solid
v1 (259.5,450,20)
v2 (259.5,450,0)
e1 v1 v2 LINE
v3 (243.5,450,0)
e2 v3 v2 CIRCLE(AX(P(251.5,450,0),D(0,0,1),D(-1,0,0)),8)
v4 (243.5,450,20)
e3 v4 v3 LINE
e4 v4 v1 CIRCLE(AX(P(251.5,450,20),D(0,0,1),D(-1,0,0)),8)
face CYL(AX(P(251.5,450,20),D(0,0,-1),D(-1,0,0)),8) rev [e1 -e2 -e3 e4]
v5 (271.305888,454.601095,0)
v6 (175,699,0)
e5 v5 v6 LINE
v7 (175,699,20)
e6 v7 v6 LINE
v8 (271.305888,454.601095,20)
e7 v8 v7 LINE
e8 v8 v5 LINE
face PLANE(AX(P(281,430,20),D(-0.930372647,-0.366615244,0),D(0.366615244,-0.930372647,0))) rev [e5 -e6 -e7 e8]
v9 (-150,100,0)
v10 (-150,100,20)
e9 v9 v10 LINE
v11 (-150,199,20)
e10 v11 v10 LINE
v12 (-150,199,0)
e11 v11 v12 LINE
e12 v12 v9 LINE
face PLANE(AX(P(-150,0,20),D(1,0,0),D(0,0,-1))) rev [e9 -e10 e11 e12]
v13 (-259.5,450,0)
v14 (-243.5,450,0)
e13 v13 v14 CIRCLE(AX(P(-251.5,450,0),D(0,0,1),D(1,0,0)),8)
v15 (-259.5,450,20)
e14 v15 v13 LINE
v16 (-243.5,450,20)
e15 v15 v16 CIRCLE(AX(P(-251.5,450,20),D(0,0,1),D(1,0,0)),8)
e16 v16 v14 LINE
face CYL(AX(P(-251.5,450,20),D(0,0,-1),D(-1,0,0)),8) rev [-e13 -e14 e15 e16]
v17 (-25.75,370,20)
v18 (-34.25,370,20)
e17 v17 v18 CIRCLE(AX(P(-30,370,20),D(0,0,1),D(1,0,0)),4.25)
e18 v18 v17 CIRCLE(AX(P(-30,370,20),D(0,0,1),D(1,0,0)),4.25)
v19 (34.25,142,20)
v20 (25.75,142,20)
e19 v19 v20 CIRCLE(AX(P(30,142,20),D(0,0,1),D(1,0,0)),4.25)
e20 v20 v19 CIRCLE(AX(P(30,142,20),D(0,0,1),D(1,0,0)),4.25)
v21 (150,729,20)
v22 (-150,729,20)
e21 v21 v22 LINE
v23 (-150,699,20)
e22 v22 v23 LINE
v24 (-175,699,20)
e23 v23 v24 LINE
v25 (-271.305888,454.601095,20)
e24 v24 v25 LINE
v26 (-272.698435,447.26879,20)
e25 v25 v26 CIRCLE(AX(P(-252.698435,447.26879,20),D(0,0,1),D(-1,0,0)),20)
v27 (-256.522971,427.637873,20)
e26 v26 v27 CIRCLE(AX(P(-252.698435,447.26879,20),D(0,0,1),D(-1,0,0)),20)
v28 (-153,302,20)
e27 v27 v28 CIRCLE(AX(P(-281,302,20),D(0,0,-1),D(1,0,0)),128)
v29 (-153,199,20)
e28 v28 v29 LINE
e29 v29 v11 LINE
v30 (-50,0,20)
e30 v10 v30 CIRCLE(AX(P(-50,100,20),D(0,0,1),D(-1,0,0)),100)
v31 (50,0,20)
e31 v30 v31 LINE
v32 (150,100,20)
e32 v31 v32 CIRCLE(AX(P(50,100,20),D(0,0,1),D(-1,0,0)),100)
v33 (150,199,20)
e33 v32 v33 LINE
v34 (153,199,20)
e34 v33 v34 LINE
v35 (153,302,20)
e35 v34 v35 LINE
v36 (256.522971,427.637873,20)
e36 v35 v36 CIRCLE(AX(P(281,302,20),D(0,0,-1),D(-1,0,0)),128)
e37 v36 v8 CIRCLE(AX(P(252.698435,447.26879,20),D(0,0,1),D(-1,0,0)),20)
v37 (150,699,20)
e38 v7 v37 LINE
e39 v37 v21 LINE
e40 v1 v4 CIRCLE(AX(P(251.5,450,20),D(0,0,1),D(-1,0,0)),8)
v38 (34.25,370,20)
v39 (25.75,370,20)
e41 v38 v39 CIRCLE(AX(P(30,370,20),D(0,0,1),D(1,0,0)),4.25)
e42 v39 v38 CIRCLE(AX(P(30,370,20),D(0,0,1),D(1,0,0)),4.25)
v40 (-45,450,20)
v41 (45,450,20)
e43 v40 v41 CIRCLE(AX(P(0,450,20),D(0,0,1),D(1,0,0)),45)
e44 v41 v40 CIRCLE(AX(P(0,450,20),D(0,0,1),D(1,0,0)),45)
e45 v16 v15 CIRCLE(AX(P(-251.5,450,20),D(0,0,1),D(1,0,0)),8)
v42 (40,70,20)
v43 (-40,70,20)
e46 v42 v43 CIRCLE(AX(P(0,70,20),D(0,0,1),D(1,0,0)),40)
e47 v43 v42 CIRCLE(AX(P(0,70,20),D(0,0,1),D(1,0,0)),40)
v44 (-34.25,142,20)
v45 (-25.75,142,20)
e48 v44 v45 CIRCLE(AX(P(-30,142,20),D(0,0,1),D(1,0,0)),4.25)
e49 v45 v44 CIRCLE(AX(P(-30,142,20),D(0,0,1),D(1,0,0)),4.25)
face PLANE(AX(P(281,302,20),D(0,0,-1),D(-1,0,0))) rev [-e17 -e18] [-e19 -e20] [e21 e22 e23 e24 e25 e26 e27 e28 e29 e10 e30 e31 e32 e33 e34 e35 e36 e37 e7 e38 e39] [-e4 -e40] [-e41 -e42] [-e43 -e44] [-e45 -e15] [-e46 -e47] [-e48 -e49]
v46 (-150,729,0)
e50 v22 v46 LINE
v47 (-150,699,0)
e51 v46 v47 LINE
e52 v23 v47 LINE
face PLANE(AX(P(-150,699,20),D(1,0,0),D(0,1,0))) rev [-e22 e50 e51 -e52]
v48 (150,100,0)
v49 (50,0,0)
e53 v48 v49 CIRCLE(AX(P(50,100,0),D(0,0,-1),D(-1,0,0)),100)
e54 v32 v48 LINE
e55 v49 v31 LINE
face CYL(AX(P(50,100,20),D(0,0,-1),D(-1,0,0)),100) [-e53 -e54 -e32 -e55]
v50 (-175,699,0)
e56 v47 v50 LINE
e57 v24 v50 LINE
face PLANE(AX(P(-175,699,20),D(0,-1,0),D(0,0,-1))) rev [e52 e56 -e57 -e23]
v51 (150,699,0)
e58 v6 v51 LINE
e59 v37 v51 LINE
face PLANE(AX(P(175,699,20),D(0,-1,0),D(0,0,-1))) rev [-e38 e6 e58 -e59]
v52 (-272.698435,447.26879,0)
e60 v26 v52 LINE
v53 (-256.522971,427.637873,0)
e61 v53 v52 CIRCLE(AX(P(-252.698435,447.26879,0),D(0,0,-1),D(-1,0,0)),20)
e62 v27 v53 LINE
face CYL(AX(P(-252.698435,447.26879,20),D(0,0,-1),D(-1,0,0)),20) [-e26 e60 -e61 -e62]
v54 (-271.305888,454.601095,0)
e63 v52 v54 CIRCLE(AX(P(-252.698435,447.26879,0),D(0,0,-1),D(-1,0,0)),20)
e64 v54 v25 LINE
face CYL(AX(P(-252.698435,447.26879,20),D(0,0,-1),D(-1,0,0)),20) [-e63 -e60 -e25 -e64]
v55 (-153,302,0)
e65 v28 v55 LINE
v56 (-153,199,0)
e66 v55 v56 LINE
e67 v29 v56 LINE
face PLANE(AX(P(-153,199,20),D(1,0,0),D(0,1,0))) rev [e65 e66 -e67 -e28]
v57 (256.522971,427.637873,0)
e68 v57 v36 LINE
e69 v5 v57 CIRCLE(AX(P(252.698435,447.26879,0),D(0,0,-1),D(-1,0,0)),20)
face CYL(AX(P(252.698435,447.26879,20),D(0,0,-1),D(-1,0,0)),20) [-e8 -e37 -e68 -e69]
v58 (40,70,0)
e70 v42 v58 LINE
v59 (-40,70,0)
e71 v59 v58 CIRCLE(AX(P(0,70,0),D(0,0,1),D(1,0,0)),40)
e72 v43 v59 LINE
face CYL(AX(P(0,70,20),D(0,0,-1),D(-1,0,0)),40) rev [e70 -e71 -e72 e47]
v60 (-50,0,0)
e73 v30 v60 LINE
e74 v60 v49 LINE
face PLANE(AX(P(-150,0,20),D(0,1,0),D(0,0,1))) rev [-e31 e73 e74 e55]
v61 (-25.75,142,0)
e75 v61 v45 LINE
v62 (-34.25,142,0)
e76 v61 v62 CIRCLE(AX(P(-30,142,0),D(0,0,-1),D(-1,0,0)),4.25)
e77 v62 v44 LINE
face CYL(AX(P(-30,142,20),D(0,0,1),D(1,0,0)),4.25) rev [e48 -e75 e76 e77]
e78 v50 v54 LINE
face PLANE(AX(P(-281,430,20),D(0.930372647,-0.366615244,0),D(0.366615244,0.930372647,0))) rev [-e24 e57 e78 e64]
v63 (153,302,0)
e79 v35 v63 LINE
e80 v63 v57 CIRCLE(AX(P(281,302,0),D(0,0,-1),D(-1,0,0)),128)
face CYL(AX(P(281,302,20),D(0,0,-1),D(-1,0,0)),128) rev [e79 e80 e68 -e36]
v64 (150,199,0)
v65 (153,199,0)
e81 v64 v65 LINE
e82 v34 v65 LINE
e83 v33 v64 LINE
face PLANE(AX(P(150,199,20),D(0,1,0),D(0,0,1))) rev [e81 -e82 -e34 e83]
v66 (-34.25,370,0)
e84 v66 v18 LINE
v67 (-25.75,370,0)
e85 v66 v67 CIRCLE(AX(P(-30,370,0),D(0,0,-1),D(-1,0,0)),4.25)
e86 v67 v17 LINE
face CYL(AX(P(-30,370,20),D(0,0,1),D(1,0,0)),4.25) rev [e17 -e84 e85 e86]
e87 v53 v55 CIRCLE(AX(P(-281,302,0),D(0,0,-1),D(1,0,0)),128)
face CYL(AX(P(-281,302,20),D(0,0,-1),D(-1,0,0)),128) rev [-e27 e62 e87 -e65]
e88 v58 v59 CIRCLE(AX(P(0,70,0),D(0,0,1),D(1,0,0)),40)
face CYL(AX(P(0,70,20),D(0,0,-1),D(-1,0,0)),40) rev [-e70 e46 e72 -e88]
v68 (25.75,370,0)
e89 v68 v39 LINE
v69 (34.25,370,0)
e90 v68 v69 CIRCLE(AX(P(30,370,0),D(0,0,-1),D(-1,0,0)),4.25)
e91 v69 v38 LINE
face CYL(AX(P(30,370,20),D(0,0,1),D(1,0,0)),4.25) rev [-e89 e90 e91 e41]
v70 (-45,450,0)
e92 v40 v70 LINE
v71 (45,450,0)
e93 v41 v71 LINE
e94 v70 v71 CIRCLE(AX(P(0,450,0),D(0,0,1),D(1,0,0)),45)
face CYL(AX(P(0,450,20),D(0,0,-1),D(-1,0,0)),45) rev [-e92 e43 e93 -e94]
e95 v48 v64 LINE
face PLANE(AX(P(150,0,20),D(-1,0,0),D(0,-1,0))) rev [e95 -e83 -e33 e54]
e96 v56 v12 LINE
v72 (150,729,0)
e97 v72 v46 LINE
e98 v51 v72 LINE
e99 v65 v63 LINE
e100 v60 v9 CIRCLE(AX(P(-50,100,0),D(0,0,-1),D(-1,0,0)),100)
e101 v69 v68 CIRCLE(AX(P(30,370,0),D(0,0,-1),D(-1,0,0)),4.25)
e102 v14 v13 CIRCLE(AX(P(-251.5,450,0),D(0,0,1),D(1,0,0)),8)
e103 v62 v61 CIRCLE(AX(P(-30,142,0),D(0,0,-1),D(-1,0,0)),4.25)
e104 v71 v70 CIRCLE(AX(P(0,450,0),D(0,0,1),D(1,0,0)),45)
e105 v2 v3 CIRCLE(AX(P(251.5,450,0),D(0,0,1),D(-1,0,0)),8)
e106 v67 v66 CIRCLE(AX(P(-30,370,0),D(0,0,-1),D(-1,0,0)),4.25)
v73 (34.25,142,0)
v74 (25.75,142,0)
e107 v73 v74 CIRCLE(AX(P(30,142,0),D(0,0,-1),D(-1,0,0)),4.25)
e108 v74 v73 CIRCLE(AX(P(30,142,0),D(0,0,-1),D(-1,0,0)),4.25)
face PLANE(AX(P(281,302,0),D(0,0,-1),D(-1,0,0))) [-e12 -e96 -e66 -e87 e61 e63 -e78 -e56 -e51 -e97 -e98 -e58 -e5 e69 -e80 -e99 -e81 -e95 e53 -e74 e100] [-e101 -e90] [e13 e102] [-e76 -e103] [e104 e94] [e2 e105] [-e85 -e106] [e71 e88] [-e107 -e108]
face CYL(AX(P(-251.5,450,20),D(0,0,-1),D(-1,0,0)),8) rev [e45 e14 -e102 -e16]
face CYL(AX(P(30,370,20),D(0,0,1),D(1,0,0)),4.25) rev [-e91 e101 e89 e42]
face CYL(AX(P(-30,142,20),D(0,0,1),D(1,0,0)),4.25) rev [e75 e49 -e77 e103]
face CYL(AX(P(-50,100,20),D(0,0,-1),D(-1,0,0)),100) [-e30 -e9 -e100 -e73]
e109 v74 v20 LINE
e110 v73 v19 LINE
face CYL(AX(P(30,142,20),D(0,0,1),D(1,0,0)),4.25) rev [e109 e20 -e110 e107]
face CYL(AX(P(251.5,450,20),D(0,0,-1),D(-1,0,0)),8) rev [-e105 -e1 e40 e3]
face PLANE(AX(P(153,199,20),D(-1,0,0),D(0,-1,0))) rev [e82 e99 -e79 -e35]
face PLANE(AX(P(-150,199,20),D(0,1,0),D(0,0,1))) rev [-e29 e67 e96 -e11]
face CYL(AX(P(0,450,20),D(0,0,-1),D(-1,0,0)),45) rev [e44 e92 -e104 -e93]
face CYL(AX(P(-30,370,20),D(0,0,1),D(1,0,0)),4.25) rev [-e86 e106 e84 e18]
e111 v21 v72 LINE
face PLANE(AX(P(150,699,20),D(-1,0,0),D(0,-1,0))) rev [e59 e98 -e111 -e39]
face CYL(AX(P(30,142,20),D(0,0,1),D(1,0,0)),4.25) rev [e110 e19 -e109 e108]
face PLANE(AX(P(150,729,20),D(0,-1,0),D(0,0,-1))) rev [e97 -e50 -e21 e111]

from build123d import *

# Parameters (mm, degrees)
SKETCH1_R           = 45
SKETCH1_R_2         = 40
SKETCH1_R_3         = 8
BOSS_EXTRUDE1_DEPTH = 20
FILLET1_R           = 100
FILLET2_R           = 20
M10_TAPPED_HOLE1_D  = 8.5


with BuildPart() as part:
    # Sketch1 → Boss-Extrude1 (new body)
    with BuildSketch(Plane.XY):
        with BuildLine():
            Line((-150, 0), (150, 0))
            Line((150, 0), (150, 199))
            Line((150, 199), (153, 199))
            Line((153, 199), (153, 302))
            ThreePointArc((153, 302), (190.490332008, 392.509667992), (281, 430))
            Line((281, 430), (175, 699))
            Line((175, 699), (150, 699))
            Line((150, 699), (150, 729))
            Line((150, 729), (-150, 729))
            Line((-150, 729), (-150, 699))
            Line((-150, 699), (-175, 699))
            Line((-175, 699), (-281, 430))
            ThreePointArc((-281, 430), (-190.490332008, 392.509667992), (-153, 302))
            Line((-153, 302), (-153, 199))
            Line((-153, 199), (-150, 199))
            Line((-150, 199), (-150, 0))
        make_face()
        with Locations((0, 450)):
            Circle(SKETCH1_R, mode=Mode.SUBTRACT)
        with Locations((0, 70)):
            Circle(SKETCH1_R_2, mode=Mode.SUBTRACT)
        with Locations((-251.5, 450)):
            Circle(SKETCH1_R_3, mode=Mode.SUBTRACT)
        with Locations(Location((251.5, 450, 0), (0, 0, 180))):
            Circle(SKETCH1_R_3, mode=Mode.SUBTRACT)
    extrude(amount=BOSS_EXTRUDE1_DEPTH)

    # Fillet1
    fillet1_edges = [part.edges().sort_by_distance(p)[0] for p in [
        (150, 0, 10),
        (-150, 0, 10),
    ]]
    fillet(fillet1_edges, radius=FILLET1_R)

    # Fillet2
    fillet2_edges = [part.edges().sort_by_distance(p)[0] for p in [
        (-281, 430, 10),
        (281, 430, 10),
    ]]
    fillet(fillet2_edges, radius=FILLET2_R)

    # M10 Tapped Hole1 (through all)
    with Locations(Plane.XY.offset(20)):
        with Locations((-30, 370), (-30, 142), (30, 142), (30, 370)):
            Hole(M10_TAPPED_HOLE1_D / 2)


solid = part.part
